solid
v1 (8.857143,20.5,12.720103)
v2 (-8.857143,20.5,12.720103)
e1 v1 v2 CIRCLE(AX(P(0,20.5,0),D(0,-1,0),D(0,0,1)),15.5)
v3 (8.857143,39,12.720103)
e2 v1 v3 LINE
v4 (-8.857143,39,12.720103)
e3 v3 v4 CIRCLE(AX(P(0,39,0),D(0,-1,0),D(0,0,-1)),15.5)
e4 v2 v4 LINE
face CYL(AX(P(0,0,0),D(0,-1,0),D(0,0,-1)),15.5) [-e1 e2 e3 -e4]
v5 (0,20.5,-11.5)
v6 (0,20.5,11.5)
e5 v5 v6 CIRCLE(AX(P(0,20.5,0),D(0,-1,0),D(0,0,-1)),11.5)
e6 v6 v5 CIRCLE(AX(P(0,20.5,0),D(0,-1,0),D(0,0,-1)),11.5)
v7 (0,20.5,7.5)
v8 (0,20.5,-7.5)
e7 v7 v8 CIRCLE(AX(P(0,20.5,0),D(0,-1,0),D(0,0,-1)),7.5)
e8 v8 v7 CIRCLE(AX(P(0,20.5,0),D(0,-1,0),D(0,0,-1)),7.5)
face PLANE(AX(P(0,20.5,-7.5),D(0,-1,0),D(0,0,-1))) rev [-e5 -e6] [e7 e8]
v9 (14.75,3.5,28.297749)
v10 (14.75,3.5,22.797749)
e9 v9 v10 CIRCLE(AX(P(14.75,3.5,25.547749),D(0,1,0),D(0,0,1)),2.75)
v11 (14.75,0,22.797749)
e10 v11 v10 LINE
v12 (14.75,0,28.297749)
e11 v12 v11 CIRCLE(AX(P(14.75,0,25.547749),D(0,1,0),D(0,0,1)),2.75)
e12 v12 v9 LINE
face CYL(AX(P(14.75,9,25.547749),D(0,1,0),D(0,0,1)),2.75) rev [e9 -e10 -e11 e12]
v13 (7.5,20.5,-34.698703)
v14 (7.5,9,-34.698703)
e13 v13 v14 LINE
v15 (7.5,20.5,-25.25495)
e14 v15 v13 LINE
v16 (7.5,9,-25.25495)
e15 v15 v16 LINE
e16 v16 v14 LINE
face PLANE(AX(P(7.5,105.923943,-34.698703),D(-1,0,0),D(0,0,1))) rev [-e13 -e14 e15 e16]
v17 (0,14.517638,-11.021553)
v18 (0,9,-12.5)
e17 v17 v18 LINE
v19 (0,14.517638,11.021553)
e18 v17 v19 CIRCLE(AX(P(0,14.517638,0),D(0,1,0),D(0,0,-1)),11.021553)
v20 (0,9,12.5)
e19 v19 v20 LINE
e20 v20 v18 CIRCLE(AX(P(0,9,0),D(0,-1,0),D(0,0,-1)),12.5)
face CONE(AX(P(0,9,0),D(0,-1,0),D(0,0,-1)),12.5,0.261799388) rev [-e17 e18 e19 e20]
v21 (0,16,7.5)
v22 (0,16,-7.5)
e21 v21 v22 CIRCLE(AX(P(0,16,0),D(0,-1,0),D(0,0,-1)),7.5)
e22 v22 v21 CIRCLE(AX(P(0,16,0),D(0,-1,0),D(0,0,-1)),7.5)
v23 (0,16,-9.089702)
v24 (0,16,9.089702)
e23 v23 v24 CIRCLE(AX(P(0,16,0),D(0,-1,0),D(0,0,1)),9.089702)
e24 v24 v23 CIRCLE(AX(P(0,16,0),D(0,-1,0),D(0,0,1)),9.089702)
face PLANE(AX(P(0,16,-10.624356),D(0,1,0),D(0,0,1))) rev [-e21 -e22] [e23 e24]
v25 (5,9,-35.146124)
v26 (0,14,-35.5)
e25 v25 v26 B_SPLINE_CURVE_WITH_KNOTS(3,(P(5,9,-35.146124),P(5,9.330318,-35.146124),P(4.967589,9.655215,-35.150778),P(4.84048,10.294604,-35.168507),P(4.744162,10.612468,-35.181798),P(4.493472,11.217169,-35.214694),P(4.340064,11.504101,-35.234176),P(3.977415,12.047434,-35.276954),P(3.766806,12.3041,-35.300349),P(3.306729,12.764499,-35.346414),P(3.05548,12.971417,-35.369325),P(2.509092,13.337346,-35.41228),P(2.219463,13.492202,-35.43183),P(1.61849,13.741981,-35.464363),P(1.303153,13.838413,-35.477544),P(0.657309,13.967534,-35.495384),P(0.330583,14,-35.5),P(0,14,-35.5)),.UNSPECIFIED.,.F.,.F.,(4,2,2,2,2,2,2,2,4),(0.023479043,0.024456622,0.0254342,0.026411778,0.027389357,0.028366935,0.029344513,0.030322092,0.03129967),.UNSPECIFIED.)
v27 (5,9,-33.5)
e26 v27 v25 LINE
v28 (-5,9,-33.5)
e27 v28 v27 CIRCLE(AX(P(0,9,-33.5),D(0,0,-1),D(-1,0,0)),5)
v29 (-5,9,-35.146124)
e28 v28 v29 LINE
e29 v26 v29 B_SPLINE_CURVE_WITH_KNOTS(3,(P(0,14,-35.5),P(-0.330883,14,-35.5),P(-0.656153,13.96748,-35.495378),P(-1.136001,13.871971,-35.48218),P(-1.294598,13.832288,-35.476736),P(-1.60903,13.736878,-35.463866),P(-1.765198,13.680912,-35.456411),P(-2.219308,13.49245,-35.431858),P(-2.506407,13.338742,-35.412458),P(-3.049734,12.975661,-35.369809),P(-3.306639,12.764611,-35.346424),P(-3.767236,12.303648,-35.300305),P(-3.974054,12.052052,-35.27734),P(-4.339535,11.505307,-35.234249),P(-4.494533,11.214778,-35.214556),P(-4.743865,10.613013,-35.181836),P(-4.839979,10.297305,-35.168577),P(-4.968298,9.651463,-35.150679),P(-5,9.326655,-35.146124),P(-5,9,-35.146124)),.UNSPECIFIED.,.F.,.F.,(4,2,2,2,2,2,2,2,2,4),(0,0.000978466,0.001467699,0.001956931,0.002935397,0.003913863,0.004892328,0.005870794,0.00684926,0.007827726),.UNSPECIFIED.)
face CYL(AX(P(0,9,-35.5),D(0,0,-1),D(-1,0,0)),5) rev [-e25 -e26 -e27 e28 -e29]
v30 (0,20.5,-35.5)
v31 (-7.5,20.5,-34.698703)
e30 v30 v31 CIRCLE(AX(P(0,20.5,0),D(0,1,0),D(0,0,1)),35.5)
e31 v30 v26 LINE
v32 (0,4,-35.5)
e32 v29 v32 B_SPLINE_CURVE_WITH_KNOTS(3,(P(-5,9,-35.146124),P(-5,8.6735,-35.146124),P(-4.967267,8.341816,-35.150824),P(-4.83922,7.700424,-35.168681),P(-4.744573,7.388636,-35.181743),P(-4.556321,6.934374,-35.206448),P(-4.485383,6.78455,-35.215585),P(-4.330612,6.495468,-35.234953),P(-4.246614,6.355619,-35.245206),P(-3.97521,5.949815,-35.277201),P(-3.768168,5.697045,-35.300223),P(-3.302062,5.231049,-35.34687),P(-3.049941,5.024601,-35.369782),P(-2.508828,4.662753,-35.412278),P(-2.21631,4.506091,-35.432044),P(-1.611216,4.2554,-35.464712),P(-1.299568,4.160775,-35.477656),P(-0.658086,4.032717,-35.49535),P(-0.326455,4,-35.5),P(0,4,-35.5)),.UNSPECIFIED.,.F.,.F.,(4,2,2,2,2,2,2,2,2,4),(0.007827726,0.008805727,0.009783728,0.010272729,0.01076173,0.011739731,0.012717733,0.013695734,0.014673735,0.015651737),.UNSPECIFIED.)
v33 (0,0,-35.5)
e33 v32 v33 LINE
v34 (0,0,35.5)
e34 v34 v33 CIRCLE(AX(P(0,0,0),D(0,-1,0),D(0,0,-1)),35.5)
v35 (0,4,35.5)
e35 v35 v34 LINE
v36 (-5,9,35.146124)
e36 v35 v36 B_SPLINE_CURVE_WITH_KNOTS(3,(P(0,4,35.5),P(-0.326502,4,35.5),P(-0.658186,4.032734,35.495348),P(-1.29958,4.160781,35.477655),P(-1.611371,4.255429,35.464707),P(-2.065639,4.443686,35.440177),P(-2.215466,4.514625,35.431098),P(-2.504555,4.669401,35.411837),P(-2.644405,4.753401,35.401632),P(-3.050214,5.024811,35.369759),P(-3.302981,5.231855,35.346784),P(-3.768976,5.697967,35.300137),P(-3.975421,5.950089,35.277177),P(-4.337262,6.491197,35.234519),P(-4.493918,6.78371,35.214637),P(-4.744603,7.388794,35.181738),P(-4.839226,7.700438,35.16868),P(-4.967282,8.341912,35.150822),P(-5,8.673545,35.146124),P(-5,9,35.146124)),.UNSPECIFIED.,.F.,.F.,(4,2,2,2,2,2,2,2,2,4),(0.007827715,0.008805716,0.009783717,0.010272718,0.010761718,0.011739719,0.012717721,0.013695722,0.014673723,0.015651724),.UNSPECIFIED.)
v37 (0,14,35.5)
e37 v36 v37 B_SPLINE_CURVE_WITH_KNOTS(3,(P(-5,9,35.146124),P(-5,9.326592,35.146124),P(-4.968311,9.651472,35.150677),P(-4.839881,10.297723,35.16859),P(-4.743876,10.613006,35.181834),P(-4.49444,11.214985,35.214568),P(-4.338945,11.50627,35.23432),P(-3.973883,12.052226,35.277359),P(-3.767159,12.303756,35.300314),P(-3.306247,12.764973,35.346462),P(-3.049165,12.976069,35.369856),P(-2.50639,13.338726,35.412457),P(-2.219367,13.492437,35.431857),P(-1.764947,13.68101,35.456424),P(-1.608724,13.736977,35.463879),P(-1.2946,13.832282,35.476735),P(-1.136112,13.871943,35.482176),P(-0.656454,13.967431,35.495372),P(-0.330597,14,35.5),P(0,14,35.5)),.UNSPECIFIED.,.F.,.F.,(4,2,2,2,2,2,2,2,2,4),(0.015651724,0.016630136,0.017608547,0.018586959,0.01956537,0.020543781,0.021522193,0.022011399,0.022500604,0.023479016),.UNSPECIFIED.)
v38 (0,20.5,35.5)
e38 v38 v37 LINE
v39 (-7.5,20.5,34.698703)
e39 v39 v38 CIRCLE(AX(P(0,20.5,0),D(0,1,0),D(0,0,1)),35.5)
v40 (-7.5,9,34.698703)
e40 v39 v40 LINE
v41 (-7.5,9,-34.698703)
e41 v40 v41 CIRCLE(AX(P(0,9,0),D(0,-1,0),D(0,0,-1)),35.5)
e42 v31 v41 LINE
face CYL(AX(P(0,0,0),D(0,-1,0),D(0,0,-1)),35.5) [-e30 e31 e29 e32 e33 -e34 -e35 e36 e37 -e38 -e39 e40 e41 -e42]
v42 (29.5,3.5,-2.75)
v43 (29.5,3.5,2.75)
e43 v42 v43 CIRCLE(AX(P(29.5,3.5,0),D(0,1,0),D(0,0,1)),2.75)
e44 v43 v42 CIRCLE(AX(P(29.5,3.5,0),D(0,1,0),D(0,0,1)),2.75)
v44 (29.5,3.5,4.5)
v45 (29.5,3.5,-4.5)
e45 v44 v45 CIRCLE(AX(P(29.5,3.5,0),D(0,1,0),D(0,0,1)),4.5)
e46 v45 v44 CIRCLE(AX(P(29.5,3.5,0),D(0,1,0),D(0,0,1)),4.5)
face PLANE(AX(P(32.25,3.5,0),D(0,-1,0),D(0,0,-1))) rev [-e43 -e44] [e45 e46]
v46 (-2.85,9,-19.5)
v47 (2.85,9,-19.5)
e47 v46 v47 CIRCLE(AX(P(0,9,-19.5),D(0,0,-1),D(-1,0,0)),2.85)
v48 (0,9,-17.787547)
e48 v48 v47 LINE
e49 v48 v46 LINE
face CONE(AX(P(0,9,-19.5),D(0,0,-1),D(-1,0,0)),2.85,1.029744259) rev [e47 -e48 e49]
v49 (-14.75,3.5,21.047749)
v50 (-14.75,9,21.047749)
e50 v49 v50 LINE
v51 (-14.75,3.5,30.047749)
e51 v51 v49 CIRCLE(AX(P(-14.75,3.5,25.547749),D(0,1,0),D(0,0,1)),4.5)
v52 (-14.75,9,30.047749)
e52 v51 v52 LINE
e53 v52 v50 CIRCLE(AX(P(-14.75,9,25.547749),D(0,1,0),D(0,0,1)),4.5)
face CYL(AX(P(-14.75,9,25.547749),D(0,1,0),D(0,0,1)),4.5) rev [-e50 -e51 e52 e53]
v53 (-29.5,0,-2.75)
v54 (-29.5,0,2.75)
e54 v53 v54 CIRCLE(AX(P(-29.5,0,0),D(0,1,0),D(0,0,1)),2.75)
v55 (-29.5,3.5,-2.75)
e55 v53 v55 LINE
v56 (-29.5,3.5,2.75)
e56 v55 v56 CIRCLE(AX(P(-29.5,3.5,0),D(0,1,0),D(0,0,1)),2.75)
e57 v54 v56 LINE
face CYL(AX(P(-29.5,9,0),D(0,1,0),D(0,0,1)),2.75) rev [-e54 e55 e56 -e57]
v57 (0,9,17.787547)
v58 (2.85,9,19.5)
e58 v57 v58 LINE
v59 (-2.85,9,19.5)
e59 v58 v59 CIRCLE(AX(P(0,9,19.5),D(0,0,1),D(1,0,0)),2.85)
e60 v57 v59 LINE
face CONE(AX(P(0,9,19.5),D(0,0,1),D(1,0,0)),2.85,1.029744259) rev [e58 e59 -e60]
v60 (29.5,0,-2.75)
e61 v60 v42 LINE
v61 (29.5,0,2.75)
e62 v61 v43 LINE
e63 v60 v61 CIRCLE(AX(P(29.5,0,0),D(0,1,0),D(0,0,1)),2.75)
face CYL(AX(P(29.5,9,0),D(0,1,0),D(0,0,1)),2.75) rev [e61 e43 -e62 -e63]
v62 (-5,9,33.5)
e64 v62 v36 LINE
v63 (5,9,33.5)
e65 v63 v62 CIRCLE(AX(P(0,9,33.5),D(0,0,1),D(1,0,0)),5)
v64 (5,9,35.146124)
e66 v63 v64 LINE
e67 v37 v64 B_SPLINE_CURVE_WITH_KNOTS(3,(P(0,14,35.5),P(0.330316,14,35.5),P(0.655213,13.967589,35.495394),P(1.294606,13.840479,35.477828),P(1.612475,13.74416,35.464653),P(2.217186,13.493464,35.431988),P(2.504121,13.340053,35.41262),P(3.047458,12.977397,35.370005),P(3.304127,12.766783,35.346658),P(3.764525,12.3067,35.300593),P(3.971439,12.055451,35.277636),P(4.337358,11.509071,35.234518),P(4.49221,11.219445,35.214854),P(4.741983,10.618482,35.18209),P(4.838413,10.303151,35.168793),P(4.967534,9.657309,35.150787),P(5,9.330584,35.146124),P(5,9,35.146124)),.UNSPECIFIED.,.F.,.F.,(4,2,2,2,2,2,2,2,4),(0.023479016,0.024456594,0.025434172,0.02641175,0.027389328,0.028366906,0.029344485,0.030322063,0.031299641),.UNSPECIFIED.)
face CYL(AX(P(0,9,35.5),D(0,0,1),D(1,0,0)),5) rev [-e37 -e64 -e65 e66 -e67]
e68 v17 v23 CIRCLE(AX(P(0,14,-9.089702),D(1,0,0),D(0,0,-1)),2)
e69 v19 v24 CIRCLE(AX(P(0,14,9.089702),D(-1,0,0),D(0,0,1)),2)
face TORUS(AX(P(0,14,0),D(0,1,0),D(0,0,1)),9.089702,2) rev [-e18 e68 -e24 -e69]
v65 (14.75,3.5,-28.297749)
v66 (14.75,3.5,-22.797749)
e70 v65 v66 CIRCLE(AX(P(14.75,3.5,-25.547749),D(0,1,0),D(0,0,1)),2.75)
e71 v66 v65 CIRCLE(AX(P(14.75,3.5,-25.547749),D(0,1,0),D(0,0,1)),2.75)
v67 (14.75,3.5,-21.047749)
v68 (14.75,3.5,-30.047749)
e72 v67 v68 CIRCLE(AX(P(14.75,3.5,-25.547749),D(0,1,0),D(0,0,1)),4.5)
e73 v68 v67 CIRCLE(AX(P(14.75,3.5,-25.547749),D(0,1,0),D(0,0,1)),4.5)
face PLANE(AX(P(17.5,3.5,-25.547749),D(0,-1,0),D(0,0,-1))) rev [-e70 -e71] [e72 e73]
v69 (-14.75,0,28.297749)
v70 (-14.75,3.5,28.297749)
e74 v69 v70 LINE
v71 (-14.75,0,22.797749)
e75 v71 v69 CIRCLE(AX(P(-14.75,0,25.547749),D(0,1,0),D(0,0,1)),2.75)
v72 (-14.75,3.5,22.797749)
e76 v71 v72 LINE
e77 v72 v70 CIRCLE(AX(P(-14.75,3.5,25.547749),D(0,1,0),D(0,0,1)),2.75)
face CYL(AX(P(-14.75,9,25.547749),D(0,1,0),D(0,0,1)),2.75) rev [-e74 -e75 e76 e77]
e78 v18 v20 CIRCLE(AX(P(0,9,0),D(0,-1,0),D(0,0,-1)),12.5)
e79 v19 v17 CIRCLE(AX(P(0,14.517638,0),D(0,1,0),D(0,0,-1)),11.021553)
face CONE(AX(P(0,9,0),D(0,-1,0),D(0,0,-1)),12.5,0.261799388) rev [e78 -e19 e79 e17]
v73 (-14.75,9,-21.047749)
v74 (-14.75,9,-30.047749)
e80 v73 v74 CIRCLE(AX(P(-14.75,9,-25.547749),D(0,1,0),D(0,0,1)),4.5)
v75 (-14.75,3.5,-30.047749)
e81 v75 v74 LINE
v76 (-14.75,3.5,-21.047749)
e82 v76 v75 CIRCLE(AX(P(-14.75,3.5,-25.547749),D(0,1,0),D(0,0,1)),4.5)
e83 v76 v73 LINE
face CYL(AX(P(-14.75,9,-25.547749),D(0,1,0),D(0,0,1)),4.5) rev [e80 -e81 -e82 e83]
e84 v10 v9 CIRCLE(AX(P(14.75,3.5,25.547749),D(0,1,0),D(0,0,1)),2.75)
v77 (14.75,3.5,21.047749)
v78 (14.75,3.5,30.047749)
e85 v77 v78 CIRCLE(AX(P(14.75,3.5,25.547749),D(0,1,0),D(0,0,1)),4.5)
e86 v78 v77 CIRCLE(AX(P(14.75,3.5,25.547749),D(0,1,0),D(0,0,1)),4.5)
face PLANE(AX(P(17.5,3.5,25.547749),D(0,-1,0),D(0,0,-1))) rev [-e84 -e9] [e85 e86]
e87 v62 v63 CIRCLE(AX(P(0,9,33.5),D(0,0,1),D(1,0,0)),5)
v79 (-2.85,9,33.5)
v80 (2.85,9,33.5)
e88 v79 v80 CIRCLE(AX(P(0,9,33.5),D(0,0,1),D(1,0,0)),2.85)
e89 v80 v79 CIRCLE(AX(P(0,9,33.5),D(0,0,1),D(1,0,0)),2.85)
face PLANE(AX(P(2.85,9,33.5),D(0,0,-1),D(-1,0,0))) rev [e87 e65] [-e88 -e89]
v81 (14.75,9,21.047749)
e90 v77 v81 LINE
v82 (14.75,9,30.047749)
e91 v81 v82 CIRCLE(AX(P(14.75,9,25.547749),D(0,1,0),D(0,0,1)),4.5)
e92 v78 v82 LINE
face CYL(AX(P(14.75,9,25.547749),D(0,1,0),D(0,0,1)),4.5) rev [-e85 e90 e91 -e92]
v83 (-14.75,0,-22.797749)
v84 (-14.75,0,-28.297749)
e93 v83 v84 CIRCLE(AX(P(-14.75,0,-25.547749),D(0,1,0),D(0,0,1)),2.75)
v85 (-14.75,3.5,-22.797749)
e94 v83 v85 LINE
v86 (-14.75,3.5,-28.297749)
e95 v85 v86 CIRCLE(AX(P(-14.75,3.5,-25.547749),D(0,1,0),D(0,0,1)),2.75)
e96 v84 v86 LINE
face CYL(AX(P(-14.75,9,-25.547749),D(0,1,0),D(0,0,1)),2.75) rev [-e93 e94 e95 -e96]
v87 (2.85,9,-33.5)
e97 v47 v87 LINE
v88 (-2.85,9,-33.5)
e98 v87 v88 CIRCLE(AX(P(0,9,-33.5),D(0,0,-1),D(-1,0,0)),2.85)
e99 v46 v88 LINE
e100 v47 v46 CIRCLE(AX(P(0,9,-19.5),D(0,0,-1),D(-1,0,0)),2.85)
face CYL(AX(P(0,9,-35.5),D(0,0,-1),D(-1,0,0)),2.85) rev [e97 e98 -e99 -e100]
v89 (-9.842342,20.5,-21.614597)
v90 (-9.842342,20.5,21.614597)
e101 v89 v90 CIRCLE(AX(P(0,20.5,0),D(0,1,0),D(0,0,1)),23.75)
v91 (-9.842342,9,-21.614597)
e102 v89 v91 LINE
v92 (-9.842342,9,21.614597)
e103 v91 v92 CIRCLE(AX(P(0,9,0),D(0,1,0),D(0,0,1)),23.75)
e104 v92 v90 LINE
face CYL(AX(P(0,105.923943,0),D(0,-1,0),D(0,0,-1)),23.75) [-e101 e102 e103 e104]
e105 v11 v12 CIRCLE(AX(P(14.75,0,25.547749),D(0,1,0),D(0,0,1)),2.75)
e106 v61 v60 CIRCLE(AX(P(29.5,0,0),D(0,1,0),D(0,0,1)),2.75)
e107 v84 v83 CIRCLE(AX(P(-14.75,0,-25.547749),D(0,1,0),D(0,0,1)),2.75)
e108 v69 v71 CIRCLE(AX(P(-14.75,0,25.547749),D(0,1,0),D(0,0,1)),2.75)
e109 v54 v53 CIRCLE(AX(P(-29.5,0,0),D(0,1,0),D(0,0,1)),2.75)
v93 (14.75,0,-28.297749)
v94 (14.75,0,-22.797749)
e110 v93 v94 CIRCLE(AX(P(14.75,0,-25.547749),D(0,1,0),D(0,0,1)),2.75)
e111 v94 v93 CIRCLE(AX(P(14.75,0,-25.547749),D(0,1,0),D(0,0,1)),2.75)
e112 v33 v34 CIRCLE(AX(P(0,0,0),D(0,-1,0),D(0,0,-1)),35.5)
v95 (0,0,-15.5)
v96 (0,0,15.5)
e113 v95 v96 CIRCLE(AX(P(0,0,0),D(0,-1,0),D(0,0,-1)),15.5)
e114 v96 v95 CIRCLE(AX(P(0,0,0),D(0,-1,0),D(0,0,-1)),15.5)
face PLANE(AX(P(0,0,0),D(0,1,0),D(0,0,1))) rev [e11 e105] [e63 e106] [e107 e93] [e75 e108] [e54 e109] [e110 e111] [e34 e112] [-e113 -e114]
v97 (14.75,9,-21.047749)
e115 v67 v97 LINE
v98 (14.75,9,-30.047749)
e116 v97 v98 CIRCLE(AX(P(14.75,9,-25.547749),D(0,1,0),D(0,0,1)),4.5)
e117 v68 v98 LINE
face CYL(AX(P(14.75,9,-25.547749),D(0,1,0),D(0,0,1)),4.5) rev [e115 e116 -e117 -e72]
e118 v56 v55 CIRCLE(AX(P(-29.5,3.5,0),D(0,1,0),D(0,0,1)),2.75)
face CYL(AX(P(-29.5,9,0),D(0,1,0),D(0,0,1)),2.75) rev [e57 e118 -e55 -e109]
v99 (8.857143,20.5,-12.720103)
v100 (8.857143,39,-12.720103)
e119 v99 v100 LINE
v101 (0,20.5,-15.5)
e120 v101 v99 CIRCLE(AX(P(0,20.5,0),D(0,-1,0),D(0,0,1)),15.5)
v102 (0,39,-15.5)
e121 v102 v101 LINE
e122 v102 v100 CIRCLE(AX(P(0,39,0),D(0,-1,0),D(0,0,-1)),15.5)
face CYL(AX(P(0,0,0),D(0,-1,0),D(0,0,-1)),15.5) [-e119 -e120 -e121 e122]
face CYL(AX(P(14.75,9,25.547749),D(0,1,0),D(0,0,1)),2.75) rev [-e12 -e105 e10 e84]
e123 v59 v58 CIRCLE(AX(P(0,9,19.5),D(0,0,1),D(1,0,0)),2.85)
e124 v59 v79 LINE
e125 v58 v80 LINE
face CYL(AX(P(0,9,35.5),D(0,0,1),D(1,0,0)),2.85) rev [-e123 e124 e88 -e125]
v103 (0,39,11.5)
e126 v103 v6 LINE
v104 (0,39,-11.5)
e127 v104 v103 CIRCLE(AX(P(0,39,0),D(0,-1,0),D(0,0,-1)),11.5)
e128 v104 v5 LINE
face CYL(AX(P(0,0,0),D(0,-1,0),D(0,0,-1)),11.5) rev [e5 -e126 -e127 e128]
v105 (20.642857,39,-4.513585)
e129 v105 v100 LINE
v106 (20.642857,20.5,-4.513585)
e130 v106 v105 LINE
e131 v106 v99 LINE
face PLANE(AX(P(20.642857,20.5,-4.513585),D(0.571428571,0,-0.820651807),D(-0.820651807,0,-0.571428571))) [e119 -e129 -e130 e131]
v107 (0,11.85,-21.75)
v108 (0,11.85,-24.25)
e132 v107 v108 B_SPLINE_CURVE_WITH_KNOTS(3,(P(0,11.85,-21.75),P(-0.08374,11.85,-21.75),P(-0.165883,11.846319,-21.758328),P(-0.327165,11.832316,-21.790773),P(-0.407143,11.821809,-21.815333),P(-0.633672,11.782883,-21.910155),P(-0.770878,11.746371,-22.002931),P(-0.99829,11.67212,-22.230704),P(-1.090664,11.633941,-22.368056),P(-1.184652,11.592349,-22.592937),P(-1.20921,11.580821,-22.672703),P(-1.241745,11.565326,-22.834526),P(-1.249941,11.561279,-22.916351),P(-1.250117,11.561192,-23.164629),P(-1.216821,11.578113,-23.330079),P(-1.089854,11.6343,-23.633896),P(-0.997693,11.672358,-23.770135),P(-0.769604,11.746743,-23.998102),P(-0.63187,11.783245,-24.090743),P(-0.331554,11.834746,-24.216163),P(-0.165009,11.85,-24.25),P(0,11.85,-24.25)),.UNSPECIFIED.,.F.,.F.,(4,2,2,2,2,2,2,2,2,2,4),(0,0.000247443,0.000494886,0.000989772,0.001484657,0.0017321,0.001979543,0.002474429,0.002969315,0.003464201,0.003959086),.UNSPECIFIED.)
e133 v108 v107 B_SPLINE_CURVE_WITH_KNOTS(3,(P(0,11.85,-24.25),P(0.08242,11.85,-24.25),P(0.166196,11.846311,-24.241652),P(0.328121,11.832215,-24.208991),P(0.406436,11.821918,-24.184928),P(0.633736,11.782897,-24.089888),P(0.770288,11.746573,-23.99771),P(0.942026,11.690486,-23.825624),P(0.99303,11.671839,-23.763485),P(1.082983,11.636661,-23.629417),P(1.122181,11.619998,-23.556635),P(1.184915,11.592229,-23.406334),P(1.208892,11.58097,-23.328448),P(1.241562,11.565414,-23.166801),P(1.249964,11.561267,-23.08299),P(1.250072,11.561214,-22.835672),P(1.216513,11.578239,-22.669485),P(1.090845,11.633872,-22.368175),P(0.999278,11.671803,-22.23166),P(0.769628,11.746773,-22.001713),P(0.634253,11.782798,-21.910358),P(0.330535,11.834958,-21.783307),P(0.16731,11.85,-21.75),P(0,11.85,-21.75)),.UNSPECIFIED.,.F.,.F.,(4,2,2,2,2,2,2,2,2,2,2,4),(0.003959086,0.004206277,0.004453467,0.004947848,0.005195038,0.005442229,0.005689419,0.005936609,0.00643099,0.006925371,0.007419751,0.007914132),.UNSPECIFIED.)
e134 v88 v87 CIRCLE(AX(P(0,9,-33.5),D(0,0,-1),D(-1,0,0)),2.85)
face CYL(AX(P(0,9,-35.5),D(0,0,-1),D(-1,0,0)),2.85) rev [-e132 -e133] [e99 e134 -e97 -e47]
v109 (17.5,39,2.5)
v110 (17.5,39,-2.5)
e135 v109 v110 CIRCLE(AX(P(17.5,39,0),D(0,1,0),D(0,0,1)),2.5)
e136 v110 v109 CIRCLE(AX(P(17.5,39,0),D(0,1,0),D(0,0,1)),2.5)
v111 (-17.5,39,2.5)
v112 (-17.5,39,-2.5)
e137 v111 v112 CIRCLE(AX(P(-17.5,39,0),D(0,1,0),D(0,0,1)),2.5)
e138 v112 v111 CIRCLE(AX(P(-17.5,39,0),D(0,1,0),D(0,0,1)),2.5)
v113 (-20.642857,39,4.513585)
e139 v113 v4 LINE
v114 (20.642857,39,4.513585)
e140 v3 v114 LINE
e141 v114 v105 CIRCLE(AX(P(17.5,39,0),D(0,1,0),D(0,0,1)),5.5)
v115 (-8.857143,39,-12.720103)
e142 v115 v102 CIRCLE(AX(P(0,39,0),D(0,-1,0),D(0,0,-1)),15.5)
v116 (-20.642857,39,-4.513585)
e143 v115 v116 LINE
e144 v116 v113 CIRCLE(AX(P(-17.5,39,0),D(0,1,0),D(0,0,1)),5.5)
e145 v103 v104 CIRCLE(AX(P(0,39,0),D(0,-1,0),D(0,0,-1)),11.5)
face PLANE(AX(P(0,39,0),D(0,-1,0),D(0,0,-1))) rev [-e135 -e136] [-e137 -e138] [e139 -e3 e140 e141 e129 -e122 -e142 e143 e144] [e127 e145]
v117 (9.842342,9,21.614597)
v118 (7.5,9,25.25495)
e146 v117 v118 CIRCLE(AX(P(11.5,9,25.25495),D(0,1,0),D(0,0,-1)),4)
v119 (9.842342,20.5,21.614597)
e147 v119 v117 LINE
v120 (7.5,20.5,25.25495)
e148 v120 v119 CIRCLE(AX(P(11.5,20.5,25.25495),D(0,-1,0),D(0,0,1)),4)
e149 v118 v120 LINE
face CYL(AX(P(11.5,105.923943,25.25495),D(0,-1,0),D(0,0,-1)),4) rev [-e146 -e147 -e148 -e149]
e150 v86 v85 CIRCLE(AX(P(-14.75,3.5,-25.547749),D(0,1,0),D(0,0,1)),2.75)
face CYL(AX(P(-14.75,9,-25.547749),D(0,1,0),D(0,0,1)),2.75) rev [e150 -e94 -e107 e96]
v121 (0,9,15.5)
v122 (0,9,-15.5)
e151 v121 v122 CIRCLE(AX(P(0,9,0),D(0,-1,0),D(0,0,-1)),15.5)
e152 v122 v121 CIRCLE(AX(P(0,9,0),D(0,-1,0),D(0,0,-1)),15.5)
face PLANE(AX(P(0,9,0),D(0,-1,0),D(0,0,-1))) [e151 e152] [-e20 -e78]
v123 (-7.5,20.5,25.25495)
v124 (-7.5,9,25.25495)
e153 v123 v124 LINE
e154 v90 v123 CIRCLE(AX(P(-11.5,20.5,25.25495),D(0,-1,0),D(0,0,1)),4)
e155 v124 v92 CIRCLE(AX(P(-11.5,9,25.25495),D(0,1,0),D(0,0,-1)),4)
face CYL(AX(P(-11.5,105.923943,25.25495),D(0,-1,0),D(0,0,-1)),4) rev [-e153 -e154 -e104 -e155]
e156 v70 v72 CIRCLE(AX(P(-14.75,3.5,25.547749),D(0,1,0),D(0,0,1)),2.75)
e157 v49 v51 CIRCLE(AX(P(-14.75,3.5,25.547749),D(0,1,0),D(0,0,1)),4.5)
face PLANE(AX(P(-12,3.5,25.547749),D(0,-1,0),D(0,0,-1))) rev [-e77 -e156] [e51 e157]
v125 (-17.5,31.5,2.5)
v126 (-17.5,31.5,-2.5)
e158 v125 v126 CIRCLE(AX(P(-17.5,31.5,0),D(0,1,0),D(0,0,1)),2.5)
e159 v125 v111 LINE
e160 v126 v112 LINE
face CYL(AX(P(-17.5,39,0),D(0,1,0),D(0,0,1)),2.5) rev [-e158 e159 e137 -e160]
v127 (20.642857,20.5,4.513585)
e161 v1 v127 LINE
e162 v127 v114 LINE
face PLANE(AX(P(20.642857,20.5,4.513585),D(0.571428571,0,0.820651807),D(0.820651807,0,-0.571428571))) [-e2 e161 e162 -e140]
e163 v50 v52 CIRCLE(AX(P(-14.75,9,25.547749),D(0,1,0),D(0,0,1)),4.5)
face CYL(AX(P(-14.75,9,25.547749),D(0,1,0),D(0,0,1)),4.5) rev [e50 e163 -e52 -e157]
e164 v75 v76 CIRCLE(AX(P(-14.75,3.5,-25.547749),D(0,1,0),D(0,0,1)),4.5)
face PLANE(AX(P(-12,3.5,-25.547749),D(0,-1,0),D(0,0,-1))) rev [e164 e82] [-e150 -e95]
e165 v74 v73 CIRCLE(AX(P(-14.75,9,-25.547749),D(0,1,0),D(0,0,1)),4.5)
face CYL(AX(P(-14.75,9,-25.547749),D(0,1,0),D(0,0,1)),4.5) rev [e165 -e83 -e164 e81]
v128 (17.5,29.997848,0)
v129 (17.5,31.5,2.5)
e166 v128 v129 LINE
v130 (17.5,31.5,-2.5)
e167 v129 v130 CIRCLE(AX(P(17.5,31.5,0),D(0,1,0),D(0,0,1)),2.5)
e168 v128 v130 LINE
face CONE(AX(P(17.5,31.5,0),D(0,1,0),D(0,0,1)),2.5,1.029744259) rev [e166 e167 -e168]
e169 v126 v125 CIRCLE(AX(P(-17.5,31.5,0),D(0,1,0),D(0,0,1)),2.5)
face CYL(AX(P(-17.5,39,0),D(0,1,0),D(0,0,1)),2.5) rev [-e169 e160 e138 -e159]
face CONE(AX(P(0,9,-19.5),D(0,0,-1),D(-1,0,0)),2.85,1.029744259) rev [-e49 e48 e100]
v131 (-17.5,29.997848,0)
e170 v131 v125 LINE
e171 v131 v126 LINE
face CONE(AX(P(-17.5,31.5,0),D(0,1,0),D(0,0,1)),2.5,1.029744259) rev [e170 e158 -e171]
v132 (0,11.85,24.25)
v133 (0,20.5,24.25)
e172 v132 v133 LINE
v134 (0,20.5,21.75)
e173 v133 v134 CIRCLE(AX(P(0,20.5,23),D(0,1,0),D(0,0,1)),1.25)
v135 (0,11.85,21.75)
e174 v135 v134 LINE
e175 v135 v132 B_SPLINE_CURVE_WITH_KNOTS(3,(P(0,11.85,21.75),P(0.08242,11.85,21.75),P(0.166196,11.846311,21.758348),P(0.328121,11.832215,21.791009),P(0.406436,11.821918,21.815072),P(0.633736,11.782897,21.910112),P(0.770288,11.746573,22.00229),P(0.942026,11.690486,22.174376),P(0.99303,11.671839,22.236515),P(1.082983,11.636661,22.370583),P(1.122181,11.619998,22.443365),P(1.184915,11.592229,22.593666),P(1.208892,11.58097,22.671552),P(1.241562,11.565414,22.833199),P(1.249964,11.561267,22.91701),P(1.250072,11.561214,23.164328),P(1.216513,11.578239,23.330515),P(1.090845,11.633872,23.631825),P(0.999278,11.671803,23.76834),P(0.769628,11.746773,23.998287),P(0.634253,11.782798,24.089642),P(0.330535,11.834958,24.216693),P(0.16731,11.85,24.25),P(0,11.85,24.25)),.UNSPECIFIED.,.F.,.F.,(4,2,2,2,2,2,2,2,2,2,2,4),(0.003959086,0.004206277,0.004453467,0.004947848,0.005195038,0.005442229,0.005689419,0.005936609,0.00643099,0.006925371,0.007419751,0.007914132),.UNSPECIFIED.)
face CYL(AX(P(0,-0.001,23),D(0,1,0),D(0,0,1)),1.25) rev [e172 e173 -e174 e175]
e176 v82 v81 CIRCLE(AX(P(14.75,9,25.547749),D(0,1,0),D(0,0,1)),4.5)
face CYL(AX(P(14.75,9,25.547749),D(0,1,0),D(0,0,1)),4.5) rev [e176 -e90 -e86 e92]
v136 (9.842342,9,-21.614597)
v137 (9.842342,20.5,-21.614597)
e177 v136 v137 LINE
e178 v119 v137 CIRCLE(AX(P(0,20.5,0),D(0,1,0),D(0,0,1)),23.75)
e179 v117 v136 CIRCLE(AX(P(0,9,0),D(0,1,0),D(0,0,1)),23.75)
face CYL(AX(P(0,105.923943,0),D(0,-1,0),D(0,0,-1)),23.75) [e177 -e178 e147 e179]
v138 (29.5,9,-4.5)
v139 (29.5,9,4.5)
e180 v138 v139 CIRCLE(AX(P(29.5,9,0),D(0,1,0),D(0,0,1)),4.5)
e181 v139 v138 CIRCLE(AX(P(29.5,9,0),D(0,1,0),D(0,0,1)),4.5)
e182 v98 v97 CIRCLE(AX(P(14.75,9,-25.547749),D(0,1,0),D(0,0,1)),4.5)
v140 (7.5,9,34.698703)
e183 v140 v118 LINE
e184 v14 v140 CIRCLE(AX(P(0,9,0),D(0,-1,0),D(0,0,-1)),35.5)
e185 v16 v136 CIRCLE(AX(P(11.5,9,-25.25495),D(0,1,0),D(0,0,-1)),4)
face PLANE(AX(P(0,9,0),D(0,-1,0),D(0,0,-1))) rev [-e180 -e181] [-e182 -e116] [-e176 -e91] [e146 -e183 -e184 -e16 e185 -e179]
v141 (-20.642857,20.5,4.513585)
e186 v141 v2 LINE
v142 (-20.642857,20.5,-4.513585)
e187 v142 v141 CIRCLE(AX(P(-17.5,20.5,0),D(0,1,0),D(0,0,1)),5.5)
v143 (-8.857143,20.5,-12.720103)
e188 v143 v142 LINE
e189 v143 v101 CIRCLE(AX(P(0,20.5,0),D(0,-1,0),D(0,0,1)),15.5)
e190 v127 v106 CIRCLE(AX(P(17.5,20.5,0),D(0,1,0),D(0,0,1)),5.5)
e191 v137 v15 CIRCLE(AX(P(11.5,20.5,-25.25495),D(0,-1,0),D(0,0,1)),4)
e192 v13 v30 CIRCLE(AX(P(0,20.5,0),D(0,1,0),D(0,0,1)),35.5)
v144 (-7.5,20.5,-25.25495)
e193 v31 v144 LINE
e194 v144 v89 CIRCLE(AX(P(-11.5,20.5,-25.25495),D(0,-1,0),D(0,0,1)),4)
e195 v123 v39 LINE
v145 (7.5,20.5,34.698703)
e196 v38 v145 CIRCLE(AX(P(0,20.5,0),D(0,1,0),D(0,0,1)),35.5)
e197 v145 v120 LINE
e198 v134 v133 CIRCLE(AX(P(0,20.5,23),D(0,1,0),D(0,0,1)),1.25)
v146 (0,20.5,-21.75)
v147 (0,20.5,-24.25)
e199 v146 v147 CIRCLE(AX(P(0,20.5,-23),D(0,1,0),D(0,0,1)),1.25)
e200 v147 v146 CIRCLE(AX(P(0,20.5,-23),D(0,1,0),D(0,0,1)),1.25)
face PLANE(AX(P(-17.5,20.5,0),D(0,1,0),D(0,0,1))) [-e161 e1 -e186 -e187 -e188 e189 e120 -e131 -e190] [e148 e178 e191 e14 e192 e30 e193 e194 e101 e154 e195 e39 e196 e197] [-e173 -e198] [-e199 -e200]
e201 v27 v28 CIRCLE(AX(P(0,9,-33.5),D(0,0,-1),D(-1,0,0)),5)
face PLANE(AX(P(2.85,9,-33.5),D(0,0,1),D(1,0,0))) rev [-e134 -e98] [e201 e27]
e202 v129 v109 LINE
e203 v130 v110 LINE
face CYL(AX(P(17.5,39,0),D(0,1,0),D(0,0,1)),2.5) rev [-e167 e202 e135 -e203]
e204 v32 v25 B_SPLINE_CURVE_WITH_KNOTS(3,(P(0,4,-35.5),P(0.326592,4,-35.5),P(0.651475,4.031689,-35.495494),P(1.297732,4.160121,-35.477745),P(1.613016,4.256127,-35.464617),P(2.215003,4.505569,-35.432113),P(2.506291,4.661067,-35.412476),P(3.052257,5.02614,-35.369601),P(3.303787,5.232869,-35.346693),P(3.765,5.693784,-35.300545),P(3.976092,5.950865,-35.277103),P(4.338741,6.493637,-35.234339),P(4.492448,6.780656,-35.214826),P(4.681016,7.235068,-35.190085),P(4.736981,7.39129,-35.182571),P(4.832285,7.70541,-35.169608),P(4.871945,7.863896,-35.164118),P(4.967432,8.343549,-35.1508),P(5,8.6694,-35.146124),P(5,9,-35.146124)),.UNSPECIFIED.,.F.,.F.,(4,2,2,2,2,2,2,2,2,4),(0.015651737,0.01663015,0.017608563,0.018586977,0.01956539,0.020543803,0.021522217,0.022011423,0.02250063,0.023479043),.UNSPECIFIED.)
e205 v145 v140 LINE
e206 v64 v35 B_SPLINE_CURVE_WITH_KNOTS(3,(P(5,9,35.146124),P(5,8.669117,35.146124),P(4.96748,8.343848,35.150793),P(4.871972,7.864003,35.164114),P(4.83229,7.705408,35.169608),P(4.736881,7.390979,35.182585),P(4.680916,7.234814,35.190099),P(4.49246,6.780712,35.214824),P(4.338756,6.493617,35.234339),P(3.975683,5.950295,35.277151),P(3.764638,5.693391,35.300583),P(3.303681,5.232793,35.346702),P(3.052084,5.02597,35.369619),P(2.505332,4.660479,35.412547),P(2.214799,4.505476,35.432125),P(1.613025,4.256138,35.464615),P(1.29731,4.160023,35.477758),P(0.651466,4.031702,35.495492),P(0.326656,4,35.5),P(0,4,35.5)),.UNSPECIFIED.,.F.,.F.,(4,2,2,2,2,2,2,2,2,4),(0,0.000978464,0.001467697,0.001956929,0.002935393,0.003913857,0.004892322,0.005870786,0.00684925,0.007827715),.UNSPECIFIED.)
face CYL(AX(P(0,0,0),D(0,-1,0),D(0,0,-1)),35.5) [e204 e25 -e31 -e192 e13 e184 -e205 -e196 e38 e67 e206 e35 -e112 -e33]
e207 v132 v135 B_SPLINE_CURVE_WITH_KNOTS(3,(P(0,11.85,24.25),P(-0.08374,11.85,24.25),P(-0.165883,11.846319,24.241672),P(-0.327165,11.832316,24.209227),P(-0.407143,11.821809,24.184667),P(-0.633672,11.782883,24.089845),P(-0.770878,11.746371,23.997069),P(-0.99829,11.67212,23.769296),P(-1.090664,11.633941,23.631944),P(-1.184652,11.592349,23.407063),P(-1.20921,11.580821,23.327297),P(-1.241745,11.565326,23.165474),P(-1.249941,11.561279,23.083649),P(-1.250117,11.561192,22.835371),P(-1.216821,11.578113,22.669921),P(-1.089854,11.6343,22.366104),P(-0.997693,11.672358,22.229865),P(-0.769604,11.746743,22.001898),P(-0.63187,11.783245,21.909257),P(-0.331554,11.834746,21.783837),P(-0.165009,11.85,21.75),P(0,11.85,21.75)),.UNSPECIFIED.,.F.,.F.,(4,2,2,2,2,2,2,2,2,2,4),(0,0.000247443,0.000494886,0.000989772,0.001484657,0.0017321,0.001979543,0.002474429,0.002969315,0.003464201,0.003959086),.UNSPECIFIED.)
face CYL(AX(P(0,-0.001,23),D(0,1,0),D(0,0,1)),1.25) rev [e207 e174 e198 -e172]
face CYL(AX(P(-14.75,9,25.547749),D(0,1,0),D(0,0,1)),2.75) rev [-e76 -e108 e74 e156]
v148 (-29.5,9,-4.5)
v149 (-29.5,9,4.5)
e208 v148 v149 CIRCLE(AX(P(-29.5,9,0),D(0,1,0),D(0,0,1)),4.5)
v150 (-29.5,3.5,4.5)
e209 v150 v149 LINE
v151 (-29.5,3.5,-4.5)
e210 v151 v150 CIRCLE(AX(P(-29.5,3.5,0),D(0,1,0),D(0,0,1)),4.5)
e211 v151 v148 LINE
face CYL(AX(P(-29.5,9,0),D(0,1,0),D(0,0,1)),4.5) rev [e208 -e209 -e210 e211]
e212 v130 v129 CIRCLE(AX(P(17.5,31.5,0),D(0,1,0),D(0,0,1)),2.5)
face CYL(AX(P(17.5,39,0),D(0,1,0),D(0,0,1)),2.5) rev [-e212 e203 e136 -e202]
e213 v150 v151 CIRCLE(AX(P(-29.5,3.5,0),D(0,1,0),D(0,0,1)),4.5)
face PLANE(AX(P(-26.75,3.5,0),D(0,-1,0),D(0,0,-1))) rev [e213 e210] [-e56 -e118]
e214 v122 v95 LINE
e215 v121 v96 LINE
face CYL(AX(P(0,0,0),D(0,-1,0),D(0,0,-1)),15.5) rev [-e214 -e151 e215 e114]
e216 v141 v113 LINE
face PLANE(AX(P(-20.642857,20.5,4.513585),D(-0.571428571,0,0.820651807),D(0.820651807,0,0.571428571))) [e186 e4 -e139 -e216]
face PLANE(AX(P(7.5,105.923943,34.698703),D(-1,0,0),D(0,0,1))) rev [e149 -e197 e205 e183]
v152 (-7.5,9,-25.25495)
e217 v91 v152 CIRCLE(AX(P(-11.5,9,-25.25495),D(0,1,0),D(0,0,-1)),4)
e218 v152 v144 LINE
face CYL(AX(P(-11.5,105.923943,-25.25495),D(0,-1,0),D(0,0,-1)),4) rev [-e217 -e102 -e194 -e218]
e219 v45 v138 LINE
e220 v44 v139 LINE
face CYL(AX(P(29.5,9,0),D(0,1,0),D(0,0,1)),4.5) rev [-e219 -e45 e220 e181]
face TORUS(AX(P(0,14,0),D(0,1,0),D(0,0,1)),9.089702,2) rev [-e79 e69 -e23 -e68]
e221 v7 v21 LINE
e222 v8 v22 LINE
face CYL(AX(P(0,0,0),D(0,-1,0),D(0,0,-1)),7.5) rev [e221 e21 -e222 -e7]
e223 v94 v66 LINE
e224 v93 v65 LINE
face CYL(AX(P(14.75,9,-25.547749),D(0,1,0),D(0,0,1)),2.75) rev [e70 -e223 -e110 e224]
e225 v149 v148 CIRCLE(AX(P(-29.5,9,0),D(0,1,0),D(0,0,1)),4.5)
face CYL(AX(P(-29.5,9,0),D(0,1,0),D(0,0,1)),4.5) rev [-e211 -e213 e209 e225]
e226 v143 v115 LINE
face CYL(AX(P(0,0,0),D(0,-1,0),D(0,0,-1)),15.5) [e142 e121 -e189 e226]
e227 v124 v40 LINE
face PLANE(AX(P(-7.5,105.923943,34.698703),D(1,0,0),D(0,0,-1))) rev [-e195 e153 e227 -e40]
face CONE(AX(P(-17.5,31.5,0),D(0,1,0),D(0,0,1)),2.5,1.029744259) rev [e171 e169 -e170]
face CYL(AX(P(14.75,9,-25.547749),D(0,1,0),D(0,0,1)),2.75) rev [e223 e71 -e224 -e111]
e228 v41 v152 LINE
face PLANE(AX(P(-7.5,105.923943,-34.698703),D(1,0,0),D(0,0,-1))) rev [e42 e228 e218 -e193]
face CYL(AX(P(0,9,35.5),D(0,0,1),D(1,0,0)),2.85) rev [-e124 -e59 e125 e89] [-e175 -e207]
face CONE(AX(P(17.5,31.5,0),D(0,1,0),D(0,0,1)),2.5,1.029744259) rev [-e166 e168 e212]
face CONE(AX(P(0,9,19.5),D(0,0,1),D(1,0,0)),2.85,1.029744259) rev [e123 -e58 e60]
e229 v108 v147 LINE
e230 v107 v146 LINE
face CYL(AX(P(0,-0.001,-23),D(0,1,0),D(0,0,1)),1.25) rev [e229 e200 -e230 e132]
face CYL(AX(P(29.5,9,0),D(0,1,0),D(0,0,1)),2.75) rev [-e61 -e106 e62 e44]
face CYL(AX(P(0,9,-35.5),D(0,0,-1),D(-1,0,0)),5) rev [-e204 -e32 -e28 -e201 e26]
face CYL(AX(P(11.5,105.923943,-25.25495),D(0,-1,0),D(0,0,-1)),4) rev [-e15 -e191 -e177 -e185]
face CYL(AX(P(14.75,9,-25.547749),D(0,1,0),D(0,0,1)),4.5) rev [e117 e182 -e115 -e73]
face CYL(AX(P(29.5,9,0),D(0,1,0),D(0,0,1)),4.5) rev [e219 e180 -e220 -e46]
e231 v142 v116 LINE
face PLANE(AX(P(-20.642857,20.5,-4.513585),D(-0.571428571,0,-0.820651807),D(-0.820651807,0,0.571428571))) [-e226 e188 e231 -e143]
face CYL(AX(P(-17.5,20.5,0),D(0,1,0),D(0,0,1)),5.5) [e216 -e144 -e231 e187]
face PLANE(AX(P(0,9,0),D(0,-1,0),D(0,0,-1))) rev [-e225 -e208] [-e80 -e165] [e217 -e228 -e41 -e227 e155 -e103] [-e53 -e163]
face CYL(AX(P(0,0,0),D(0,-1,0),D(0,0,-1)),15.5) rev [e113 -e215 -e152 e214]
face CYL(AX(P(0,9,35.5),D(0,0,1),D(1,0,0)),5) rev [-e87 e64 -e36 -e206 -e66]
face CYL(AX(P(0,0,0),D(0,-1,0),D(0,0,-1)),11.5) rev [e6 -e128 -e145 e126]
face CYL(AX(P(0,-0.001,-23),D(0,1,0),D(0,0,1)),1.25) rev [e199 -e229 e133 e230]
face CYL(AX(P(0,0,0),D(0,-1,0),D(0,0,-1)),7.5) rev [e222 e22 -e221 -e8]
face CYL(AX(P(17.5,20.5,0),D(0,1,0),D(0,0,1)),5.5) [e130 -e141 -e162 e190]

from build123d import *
from build123d.topology import SkipClean

# Parameters (mm, degrees)
SIDE_LUG_PROFILE_R                         = 7.5
SIDE_LUGS_DEPTH                            = 18.5
OVAL_MOUNTING_BOSS_DEPTH                   = 11.5
BOSS_EDGE_FILLET_R4_R                      = 4
FLANGE_HOLES_6X_C_BORE_5_5_D               = 5.5
FLANGE_HOLES_6X_C_BORE_5_5_CBORE_D         = 9
FLANGE_HOLES_6X_C_BORE_5_5_CBORE_DEPTH     = 5.5
SIDE_PORT_C_BORE_5_7_D                     = 5.7
SIDE_PORT_C_BORE_5_7_DEPTH                 = 16
SIDE_PORT_C_BORE_5_7_CBORE_D               = 10
SIDE_PORT_C_BORE_5_7_CBORE_DEPTH           = 2
SIDE_PORT_C_BORE_5_7_TIP                   = 1.712452764228547
SIDE_PORT_C_BORE_5_7_ON_FACE_2_D           = 5.7
SIDE_PORT_C_BORE_5_7_ON_FACE_2_DEPTH       = 16
SIDE_PORT_C_BORE_5_7_ON_FACE_2_CBORE_D     = 10
SIDE_PORT_C_BORE_5_7_ON_FACE_2_CBORE_DEPTH = 2
SIDE_PORT_C_BORE_5_7_ON_FACE_2_TIP         = 1.712452764228547
RELIEF_CUT_REACH                           = 56.229
RELIEF_CUT_END_RADIUS                      = 2.850000000000001
RELIEF_CUT_PROFILE_R                       = 1.250000000000001
RELIEF_CUT_PROFILE_R_2                     = 1.2500000000000009
LUG_DRILL_HOLES_5_D                        = 5
LUG_DRILL_HOLES_5_DEPTH                    = 7.5
LUG_DRILL_HOLES_5_TIP                      = 1.5021515475689007
BORE_EDGE_FILLET_R2_R                      = 2


with BuildPart() as part:
    # Flange Body Profile → Flange Body (revolve)
    with BuildSketch(Plane(origin=(0, 0, 0), x_dir=(0, 0, -1), z_dir=(1, 0, 0))):
        Polygon((15.5, 39), (15.500000000000002, 9), (12.5, 9), (10.624355652982135, 16), (7.5, 16), (7.5, 20.5), (11.5, 20.5), (11.5, 39), align=None)
        Polygon((35.5, 9.1e-16), (15.5, -2.45e-15), (15.500000000000002, 9), (35.5, 9.000000000000002), align=None)
    revolve(axis=Axis((0, 0, 0), (0, 1, 0)))

    # Side Lug Profile → Side Lugs (add)
    with SkipClean():  # the faces are left unmerged after this step: merging them gives an invalid solid
        with BuildSketch(Plane(origin=(0, 39, 0), x_dir=(1, 0, 0), z_dir=(0, 1, 0))):
            with BuildLine():
                Line((-20.642857142857142, 4.513584936565594), (-8.857142857142858, 12.720103003048491))
                ThreePointArc((-8.857142857142858, 12.720103003048491), (-2.49e-15, 15.499999999999995), (8.85714285714285, 12.720103003048491))
                Line((8.85714285714285, 12.720103003048491), (20.642857142857142, 4.513584936565599))
                ThreePointArc((20.642857142857142, 4.513584936565599), (23, 6.43e-15), (20.642857142857142, -4.513584936565586))
                Line((20.642857142857142, -4.513584936565586), (8.857142857142858, -12.720103003048482))
                ThreePointArc((8.857142857142858, -12.720103003048482), (9.5e-16, -15.499999999999996), (-8.857142857142854, -12.72010300304849))
                Line((-8.857142857142854, -12.72010300304849), (-20.642857142857142, -4.513584936565596))
                ThreePointArc((-20.642857142857142, -4.513584936565596), (-23, 6.7e-16), (-20.642857142857142, 4.513584936565594))
            make_face()
            with Locations(Location((0, 0, 0), (0, 0, 90))):
                Circle(SIDE_LUG_PROFILE_R, mode=Mode.SUBTRACT)
        extrude(amount=-SIDE_LUGS_DEPTH)

    # Oval Boss Profile → Oval Mounting Boss (add)
    with BuildSketch(Plane(origin=(0, 9.000000000000002, 0), x_dir=(1, 0, 0), z_dir=(0, 1, 0))):
        with BuildLine():
            Line((7.500000000000008, -34.69870314579495), (7.500000000000008, -22.534695471649933))
            ThreePointArc((7.500000000000008, -22.534695471649933), (23.750000000000004, 0), (7.500000000000008, 22.534695471649933))
            Line((7.500000000000008, 22.534695471649933), (7.500000000000008, 34.69870314579495))
            ThreePointArc((7.500000000000008, 34.69870314579495), (2.17e-15, 35.50000000000001), (-7.499999999999991, 34.69870314579495))
            Line((-7.499999999999991, 34.69870314579495), (-7.499999999999995, 22.534695471649936))
            ThreePointArc((-7.499999999999995, 22.534695471649936), (-23.75, 2.91e-15), (-7.499999999999995, -22.534695471649936))
            Line((-7.499999999999995, -22.534695471649936), (-7.499999999999991, -34.69870314579495))
            ThreePointArc((-7.499999999999991, -34.69870314579495), (2.17e-15, -35.50000000000001), (7.500000000000008, -34.69870314579495))
        make_face()
    extrude(amount=OVAL_MOUNTING_BOSS_DEPTH)

    # Boss Edge Fillet R4
    boss_edge_fillet_r4_edges = [part.edges().sort_by_distance(p)[0] for p in [
        (-7.499999999999995, 14.750000000000002, -22.534695471649933),
        (-7.499999999999998, 14.750000000000002, 22.534695471649936),
        (7.500000000000009, 14.750000000000002, 22.534695471649933),
        (7.500000000000007, 14.750000000000002, -22.534695471649933),
    ]]
    fillet(boss_edge_fillet_r4_edges, radius=BOSS_EDGE_FILLET_R4_R)

    # Flange Holes 6x C'bore Ø5.5 (through all)
    with Locations(Plane(origin=(0, 9.000000000000002, 0), x_dir=(1, 0, 0), z_dir=(0, 1, 0))):
        with Locations((-14.75, -25.547749412), (-29.5, 0), (-14.75, 25.547749412), (14.75, 25.547749412), (29.5, 0), (14.75, -25.547749412)):
            CounterBoreHole(FLANGE_HOLES_6X_C_BORE_5_5_D / 2, FLANGE_HOLES_6X_C_BORE_5_5_CBORE_D / 2, FLANGE_HOLES_6X_C_BORE_5_5_CBORE_DEPTH)

    # Side Port C'bore Ø5.7
    with Locations(Plane(origin=(0, 9, 35.5), x_dir=(1, 0, 0), z_dir=(0, 0, 1))):
        with Locations((0, 0)):
            CounterBoreHole(SIDE_PORT_C_BORE_5_7_D / 2, SIDE_PORT_C_BORE_5_7_CBORE_D / 2, SIDE_PORT_C_BORE_5_7_CBORE_DEPTH, depth=SIDE_PORT_C_BORE_5_7_DEPTH)
            with Locations((0, 0, -(SIDE_PORT_C_BORE_5_7_DEPTH + SIDE_PORT_C_BORE_5_7_TIP / 2))):  # 118° drill point
                Cone(0, SIDE_PORT_C_BORE_5_7_D / 2, SIDE_PORT_C_BORE_5_7_TIP, mode=Mode.SUBTRACT)

    # Side Port C'bore Ø5.7 on face 2
    with Locations(Plane(origin=(0, 9, -35.5), x_dir=(-1, 0, 0), z_dir=(0, 0, -1))):
        with Locations((0, 0)):
            CounterBoreHole(SIDE_PORT_C_BORE_5_7_ON_FACE_2_D / 2, SIDE_PORT_C_BORE_5_7_ON_FACE_2_CBORE_D / 2, SIDE_PORT_C_BORE_5_7_ON_FACE_2_CBORE_DEPTH, depth=SIDE_PORT_C_BORE_5_7_ON_FACE_2_DEPTH)
            with Locations((0, 0, -(SIDE_PORT_C_BORE_5_7_ON_FACE_2_DEPTH + SIDE_PORT_C_BORE_5_7_ON_FACE_2_TIP / 2))):  # 118° drill point
                Cone(0, SIDE_PORT_C_BORE_5_7_ON_FACE_2_D / 2, SIDE_PORT_C_BORE_5_7_ON_FACE_2_TIP, mode=Mode.SUBTRACT)

    # Relief Cut: up to this cylinder (the profile starts outside it)
    relief_cut_end = Plane(origin=(0, 9, 0), z_dir=(0, 0, -1)) * Cylinder(RELIEF_CUT_END_RADIUS, 165.158, mode=Mode.PRIVATE)
    # Relief Cut Profile → Relief Cut (cut, up to the surface)
    with BuildSketch(Plane(origin=(0, 20.5, 0), x_dir=(1, 0, 0), z_dir=(0, 1, 0)), mode=Mode.PRIVATE) as relief_cut_sk1:
        with Locations(Location((-8.24e-15, 23, 0), (0, 0, 270))):
            Circle(RELIEF_CUT_PROFILE_R)
    relief_cut_tool1 = extrude(relief_cut_sk1.sketch, amount=-RELIEF_CUT_REACH, mode=Mode.PRIVATE) - relief_cut_end
    add(relief_cut_tool1.solids().sort_by_distance((0, 20.5, -23))[0], mode=Mode.SUBTRACT)
    # Relief Cut Profile → Relief Cut (cut, up to the surface)
    with BuildSketch(Plane(origin=(0, 20.5, 0), x_dir=(1, 0, 0), z_dir=(0, 1, 0)), mode=Mode.PRIVATE) as relief_cut_sk2:
        with Locations(Location((5.64e-15, -23, 0), (0, 0, 270))):
            Circle(RELIEF_CUT_PROFILE_R_2)
    relief_cut_tool2 = extrude(relief_cut_sk2.sketch, amount=-RELIEF_CUT_REACH, mode=Mode.PRIVATE) - relief_cut_end
    add(relief_cut_tool2.solids().sort_by_distance((0, 20.5, 23))[0], mode=Mode.SUBTRACT)

    # Lug Drill Holes Ø5
    with Locations(Plane(origin=(0, 39, 0), x_dir=(1, 0, 0), z_dir=(0, 1, 0))):
        with Locations((-17.5, 0), (17.5, 0)):
            Hole(LUG_DRILL_HOLES_5_D / 2, depth=LUG_DRILL_HOLES_5_DEPTH)
            with Locations((0, 0, -(LUG_DRILL_HOLES_5_DEPTH + LUG_DRILL_HOLES_5_TIP / 2))):  # 118° drill point
                Cone(0, LUG_DRILL_HOLES_5_D / 2, LUG_DRILL_HOLES_5_TIP, mode=Mode.SUBTRACT)

    # Central Bore Profile → Central Bore (revolve, cut)
    with BuildSketch(Plane(origin=(0, 0, 0), x_dir=(0, 0, -1), z_dir=(1, 0, 0))):
        Polygon((12.5, 9), (0, 8.999999999999998), (0, 39), (11.5, 39), (11.5, 20.5), (7.5, 20.5), (7.5, 16), (10.624355652982135, 16), align=None)
    revolve(axis=Axis((0, 0, 0), (0, 1, 0)), mode=Mode.SUBTRACT)

    # Bore Edge Fillet R2
    bore_edge_fillet_r2_edges = [part.edges().sort_by_distance(p)[0] for p in [
        (-1.3e-15, 16, 10.624355652982135),
    ]]
    fillet(bore_edge_fillet_r2_edges, radius=BORE_EDGE_FILLET_R2_R)


solid = part.part
